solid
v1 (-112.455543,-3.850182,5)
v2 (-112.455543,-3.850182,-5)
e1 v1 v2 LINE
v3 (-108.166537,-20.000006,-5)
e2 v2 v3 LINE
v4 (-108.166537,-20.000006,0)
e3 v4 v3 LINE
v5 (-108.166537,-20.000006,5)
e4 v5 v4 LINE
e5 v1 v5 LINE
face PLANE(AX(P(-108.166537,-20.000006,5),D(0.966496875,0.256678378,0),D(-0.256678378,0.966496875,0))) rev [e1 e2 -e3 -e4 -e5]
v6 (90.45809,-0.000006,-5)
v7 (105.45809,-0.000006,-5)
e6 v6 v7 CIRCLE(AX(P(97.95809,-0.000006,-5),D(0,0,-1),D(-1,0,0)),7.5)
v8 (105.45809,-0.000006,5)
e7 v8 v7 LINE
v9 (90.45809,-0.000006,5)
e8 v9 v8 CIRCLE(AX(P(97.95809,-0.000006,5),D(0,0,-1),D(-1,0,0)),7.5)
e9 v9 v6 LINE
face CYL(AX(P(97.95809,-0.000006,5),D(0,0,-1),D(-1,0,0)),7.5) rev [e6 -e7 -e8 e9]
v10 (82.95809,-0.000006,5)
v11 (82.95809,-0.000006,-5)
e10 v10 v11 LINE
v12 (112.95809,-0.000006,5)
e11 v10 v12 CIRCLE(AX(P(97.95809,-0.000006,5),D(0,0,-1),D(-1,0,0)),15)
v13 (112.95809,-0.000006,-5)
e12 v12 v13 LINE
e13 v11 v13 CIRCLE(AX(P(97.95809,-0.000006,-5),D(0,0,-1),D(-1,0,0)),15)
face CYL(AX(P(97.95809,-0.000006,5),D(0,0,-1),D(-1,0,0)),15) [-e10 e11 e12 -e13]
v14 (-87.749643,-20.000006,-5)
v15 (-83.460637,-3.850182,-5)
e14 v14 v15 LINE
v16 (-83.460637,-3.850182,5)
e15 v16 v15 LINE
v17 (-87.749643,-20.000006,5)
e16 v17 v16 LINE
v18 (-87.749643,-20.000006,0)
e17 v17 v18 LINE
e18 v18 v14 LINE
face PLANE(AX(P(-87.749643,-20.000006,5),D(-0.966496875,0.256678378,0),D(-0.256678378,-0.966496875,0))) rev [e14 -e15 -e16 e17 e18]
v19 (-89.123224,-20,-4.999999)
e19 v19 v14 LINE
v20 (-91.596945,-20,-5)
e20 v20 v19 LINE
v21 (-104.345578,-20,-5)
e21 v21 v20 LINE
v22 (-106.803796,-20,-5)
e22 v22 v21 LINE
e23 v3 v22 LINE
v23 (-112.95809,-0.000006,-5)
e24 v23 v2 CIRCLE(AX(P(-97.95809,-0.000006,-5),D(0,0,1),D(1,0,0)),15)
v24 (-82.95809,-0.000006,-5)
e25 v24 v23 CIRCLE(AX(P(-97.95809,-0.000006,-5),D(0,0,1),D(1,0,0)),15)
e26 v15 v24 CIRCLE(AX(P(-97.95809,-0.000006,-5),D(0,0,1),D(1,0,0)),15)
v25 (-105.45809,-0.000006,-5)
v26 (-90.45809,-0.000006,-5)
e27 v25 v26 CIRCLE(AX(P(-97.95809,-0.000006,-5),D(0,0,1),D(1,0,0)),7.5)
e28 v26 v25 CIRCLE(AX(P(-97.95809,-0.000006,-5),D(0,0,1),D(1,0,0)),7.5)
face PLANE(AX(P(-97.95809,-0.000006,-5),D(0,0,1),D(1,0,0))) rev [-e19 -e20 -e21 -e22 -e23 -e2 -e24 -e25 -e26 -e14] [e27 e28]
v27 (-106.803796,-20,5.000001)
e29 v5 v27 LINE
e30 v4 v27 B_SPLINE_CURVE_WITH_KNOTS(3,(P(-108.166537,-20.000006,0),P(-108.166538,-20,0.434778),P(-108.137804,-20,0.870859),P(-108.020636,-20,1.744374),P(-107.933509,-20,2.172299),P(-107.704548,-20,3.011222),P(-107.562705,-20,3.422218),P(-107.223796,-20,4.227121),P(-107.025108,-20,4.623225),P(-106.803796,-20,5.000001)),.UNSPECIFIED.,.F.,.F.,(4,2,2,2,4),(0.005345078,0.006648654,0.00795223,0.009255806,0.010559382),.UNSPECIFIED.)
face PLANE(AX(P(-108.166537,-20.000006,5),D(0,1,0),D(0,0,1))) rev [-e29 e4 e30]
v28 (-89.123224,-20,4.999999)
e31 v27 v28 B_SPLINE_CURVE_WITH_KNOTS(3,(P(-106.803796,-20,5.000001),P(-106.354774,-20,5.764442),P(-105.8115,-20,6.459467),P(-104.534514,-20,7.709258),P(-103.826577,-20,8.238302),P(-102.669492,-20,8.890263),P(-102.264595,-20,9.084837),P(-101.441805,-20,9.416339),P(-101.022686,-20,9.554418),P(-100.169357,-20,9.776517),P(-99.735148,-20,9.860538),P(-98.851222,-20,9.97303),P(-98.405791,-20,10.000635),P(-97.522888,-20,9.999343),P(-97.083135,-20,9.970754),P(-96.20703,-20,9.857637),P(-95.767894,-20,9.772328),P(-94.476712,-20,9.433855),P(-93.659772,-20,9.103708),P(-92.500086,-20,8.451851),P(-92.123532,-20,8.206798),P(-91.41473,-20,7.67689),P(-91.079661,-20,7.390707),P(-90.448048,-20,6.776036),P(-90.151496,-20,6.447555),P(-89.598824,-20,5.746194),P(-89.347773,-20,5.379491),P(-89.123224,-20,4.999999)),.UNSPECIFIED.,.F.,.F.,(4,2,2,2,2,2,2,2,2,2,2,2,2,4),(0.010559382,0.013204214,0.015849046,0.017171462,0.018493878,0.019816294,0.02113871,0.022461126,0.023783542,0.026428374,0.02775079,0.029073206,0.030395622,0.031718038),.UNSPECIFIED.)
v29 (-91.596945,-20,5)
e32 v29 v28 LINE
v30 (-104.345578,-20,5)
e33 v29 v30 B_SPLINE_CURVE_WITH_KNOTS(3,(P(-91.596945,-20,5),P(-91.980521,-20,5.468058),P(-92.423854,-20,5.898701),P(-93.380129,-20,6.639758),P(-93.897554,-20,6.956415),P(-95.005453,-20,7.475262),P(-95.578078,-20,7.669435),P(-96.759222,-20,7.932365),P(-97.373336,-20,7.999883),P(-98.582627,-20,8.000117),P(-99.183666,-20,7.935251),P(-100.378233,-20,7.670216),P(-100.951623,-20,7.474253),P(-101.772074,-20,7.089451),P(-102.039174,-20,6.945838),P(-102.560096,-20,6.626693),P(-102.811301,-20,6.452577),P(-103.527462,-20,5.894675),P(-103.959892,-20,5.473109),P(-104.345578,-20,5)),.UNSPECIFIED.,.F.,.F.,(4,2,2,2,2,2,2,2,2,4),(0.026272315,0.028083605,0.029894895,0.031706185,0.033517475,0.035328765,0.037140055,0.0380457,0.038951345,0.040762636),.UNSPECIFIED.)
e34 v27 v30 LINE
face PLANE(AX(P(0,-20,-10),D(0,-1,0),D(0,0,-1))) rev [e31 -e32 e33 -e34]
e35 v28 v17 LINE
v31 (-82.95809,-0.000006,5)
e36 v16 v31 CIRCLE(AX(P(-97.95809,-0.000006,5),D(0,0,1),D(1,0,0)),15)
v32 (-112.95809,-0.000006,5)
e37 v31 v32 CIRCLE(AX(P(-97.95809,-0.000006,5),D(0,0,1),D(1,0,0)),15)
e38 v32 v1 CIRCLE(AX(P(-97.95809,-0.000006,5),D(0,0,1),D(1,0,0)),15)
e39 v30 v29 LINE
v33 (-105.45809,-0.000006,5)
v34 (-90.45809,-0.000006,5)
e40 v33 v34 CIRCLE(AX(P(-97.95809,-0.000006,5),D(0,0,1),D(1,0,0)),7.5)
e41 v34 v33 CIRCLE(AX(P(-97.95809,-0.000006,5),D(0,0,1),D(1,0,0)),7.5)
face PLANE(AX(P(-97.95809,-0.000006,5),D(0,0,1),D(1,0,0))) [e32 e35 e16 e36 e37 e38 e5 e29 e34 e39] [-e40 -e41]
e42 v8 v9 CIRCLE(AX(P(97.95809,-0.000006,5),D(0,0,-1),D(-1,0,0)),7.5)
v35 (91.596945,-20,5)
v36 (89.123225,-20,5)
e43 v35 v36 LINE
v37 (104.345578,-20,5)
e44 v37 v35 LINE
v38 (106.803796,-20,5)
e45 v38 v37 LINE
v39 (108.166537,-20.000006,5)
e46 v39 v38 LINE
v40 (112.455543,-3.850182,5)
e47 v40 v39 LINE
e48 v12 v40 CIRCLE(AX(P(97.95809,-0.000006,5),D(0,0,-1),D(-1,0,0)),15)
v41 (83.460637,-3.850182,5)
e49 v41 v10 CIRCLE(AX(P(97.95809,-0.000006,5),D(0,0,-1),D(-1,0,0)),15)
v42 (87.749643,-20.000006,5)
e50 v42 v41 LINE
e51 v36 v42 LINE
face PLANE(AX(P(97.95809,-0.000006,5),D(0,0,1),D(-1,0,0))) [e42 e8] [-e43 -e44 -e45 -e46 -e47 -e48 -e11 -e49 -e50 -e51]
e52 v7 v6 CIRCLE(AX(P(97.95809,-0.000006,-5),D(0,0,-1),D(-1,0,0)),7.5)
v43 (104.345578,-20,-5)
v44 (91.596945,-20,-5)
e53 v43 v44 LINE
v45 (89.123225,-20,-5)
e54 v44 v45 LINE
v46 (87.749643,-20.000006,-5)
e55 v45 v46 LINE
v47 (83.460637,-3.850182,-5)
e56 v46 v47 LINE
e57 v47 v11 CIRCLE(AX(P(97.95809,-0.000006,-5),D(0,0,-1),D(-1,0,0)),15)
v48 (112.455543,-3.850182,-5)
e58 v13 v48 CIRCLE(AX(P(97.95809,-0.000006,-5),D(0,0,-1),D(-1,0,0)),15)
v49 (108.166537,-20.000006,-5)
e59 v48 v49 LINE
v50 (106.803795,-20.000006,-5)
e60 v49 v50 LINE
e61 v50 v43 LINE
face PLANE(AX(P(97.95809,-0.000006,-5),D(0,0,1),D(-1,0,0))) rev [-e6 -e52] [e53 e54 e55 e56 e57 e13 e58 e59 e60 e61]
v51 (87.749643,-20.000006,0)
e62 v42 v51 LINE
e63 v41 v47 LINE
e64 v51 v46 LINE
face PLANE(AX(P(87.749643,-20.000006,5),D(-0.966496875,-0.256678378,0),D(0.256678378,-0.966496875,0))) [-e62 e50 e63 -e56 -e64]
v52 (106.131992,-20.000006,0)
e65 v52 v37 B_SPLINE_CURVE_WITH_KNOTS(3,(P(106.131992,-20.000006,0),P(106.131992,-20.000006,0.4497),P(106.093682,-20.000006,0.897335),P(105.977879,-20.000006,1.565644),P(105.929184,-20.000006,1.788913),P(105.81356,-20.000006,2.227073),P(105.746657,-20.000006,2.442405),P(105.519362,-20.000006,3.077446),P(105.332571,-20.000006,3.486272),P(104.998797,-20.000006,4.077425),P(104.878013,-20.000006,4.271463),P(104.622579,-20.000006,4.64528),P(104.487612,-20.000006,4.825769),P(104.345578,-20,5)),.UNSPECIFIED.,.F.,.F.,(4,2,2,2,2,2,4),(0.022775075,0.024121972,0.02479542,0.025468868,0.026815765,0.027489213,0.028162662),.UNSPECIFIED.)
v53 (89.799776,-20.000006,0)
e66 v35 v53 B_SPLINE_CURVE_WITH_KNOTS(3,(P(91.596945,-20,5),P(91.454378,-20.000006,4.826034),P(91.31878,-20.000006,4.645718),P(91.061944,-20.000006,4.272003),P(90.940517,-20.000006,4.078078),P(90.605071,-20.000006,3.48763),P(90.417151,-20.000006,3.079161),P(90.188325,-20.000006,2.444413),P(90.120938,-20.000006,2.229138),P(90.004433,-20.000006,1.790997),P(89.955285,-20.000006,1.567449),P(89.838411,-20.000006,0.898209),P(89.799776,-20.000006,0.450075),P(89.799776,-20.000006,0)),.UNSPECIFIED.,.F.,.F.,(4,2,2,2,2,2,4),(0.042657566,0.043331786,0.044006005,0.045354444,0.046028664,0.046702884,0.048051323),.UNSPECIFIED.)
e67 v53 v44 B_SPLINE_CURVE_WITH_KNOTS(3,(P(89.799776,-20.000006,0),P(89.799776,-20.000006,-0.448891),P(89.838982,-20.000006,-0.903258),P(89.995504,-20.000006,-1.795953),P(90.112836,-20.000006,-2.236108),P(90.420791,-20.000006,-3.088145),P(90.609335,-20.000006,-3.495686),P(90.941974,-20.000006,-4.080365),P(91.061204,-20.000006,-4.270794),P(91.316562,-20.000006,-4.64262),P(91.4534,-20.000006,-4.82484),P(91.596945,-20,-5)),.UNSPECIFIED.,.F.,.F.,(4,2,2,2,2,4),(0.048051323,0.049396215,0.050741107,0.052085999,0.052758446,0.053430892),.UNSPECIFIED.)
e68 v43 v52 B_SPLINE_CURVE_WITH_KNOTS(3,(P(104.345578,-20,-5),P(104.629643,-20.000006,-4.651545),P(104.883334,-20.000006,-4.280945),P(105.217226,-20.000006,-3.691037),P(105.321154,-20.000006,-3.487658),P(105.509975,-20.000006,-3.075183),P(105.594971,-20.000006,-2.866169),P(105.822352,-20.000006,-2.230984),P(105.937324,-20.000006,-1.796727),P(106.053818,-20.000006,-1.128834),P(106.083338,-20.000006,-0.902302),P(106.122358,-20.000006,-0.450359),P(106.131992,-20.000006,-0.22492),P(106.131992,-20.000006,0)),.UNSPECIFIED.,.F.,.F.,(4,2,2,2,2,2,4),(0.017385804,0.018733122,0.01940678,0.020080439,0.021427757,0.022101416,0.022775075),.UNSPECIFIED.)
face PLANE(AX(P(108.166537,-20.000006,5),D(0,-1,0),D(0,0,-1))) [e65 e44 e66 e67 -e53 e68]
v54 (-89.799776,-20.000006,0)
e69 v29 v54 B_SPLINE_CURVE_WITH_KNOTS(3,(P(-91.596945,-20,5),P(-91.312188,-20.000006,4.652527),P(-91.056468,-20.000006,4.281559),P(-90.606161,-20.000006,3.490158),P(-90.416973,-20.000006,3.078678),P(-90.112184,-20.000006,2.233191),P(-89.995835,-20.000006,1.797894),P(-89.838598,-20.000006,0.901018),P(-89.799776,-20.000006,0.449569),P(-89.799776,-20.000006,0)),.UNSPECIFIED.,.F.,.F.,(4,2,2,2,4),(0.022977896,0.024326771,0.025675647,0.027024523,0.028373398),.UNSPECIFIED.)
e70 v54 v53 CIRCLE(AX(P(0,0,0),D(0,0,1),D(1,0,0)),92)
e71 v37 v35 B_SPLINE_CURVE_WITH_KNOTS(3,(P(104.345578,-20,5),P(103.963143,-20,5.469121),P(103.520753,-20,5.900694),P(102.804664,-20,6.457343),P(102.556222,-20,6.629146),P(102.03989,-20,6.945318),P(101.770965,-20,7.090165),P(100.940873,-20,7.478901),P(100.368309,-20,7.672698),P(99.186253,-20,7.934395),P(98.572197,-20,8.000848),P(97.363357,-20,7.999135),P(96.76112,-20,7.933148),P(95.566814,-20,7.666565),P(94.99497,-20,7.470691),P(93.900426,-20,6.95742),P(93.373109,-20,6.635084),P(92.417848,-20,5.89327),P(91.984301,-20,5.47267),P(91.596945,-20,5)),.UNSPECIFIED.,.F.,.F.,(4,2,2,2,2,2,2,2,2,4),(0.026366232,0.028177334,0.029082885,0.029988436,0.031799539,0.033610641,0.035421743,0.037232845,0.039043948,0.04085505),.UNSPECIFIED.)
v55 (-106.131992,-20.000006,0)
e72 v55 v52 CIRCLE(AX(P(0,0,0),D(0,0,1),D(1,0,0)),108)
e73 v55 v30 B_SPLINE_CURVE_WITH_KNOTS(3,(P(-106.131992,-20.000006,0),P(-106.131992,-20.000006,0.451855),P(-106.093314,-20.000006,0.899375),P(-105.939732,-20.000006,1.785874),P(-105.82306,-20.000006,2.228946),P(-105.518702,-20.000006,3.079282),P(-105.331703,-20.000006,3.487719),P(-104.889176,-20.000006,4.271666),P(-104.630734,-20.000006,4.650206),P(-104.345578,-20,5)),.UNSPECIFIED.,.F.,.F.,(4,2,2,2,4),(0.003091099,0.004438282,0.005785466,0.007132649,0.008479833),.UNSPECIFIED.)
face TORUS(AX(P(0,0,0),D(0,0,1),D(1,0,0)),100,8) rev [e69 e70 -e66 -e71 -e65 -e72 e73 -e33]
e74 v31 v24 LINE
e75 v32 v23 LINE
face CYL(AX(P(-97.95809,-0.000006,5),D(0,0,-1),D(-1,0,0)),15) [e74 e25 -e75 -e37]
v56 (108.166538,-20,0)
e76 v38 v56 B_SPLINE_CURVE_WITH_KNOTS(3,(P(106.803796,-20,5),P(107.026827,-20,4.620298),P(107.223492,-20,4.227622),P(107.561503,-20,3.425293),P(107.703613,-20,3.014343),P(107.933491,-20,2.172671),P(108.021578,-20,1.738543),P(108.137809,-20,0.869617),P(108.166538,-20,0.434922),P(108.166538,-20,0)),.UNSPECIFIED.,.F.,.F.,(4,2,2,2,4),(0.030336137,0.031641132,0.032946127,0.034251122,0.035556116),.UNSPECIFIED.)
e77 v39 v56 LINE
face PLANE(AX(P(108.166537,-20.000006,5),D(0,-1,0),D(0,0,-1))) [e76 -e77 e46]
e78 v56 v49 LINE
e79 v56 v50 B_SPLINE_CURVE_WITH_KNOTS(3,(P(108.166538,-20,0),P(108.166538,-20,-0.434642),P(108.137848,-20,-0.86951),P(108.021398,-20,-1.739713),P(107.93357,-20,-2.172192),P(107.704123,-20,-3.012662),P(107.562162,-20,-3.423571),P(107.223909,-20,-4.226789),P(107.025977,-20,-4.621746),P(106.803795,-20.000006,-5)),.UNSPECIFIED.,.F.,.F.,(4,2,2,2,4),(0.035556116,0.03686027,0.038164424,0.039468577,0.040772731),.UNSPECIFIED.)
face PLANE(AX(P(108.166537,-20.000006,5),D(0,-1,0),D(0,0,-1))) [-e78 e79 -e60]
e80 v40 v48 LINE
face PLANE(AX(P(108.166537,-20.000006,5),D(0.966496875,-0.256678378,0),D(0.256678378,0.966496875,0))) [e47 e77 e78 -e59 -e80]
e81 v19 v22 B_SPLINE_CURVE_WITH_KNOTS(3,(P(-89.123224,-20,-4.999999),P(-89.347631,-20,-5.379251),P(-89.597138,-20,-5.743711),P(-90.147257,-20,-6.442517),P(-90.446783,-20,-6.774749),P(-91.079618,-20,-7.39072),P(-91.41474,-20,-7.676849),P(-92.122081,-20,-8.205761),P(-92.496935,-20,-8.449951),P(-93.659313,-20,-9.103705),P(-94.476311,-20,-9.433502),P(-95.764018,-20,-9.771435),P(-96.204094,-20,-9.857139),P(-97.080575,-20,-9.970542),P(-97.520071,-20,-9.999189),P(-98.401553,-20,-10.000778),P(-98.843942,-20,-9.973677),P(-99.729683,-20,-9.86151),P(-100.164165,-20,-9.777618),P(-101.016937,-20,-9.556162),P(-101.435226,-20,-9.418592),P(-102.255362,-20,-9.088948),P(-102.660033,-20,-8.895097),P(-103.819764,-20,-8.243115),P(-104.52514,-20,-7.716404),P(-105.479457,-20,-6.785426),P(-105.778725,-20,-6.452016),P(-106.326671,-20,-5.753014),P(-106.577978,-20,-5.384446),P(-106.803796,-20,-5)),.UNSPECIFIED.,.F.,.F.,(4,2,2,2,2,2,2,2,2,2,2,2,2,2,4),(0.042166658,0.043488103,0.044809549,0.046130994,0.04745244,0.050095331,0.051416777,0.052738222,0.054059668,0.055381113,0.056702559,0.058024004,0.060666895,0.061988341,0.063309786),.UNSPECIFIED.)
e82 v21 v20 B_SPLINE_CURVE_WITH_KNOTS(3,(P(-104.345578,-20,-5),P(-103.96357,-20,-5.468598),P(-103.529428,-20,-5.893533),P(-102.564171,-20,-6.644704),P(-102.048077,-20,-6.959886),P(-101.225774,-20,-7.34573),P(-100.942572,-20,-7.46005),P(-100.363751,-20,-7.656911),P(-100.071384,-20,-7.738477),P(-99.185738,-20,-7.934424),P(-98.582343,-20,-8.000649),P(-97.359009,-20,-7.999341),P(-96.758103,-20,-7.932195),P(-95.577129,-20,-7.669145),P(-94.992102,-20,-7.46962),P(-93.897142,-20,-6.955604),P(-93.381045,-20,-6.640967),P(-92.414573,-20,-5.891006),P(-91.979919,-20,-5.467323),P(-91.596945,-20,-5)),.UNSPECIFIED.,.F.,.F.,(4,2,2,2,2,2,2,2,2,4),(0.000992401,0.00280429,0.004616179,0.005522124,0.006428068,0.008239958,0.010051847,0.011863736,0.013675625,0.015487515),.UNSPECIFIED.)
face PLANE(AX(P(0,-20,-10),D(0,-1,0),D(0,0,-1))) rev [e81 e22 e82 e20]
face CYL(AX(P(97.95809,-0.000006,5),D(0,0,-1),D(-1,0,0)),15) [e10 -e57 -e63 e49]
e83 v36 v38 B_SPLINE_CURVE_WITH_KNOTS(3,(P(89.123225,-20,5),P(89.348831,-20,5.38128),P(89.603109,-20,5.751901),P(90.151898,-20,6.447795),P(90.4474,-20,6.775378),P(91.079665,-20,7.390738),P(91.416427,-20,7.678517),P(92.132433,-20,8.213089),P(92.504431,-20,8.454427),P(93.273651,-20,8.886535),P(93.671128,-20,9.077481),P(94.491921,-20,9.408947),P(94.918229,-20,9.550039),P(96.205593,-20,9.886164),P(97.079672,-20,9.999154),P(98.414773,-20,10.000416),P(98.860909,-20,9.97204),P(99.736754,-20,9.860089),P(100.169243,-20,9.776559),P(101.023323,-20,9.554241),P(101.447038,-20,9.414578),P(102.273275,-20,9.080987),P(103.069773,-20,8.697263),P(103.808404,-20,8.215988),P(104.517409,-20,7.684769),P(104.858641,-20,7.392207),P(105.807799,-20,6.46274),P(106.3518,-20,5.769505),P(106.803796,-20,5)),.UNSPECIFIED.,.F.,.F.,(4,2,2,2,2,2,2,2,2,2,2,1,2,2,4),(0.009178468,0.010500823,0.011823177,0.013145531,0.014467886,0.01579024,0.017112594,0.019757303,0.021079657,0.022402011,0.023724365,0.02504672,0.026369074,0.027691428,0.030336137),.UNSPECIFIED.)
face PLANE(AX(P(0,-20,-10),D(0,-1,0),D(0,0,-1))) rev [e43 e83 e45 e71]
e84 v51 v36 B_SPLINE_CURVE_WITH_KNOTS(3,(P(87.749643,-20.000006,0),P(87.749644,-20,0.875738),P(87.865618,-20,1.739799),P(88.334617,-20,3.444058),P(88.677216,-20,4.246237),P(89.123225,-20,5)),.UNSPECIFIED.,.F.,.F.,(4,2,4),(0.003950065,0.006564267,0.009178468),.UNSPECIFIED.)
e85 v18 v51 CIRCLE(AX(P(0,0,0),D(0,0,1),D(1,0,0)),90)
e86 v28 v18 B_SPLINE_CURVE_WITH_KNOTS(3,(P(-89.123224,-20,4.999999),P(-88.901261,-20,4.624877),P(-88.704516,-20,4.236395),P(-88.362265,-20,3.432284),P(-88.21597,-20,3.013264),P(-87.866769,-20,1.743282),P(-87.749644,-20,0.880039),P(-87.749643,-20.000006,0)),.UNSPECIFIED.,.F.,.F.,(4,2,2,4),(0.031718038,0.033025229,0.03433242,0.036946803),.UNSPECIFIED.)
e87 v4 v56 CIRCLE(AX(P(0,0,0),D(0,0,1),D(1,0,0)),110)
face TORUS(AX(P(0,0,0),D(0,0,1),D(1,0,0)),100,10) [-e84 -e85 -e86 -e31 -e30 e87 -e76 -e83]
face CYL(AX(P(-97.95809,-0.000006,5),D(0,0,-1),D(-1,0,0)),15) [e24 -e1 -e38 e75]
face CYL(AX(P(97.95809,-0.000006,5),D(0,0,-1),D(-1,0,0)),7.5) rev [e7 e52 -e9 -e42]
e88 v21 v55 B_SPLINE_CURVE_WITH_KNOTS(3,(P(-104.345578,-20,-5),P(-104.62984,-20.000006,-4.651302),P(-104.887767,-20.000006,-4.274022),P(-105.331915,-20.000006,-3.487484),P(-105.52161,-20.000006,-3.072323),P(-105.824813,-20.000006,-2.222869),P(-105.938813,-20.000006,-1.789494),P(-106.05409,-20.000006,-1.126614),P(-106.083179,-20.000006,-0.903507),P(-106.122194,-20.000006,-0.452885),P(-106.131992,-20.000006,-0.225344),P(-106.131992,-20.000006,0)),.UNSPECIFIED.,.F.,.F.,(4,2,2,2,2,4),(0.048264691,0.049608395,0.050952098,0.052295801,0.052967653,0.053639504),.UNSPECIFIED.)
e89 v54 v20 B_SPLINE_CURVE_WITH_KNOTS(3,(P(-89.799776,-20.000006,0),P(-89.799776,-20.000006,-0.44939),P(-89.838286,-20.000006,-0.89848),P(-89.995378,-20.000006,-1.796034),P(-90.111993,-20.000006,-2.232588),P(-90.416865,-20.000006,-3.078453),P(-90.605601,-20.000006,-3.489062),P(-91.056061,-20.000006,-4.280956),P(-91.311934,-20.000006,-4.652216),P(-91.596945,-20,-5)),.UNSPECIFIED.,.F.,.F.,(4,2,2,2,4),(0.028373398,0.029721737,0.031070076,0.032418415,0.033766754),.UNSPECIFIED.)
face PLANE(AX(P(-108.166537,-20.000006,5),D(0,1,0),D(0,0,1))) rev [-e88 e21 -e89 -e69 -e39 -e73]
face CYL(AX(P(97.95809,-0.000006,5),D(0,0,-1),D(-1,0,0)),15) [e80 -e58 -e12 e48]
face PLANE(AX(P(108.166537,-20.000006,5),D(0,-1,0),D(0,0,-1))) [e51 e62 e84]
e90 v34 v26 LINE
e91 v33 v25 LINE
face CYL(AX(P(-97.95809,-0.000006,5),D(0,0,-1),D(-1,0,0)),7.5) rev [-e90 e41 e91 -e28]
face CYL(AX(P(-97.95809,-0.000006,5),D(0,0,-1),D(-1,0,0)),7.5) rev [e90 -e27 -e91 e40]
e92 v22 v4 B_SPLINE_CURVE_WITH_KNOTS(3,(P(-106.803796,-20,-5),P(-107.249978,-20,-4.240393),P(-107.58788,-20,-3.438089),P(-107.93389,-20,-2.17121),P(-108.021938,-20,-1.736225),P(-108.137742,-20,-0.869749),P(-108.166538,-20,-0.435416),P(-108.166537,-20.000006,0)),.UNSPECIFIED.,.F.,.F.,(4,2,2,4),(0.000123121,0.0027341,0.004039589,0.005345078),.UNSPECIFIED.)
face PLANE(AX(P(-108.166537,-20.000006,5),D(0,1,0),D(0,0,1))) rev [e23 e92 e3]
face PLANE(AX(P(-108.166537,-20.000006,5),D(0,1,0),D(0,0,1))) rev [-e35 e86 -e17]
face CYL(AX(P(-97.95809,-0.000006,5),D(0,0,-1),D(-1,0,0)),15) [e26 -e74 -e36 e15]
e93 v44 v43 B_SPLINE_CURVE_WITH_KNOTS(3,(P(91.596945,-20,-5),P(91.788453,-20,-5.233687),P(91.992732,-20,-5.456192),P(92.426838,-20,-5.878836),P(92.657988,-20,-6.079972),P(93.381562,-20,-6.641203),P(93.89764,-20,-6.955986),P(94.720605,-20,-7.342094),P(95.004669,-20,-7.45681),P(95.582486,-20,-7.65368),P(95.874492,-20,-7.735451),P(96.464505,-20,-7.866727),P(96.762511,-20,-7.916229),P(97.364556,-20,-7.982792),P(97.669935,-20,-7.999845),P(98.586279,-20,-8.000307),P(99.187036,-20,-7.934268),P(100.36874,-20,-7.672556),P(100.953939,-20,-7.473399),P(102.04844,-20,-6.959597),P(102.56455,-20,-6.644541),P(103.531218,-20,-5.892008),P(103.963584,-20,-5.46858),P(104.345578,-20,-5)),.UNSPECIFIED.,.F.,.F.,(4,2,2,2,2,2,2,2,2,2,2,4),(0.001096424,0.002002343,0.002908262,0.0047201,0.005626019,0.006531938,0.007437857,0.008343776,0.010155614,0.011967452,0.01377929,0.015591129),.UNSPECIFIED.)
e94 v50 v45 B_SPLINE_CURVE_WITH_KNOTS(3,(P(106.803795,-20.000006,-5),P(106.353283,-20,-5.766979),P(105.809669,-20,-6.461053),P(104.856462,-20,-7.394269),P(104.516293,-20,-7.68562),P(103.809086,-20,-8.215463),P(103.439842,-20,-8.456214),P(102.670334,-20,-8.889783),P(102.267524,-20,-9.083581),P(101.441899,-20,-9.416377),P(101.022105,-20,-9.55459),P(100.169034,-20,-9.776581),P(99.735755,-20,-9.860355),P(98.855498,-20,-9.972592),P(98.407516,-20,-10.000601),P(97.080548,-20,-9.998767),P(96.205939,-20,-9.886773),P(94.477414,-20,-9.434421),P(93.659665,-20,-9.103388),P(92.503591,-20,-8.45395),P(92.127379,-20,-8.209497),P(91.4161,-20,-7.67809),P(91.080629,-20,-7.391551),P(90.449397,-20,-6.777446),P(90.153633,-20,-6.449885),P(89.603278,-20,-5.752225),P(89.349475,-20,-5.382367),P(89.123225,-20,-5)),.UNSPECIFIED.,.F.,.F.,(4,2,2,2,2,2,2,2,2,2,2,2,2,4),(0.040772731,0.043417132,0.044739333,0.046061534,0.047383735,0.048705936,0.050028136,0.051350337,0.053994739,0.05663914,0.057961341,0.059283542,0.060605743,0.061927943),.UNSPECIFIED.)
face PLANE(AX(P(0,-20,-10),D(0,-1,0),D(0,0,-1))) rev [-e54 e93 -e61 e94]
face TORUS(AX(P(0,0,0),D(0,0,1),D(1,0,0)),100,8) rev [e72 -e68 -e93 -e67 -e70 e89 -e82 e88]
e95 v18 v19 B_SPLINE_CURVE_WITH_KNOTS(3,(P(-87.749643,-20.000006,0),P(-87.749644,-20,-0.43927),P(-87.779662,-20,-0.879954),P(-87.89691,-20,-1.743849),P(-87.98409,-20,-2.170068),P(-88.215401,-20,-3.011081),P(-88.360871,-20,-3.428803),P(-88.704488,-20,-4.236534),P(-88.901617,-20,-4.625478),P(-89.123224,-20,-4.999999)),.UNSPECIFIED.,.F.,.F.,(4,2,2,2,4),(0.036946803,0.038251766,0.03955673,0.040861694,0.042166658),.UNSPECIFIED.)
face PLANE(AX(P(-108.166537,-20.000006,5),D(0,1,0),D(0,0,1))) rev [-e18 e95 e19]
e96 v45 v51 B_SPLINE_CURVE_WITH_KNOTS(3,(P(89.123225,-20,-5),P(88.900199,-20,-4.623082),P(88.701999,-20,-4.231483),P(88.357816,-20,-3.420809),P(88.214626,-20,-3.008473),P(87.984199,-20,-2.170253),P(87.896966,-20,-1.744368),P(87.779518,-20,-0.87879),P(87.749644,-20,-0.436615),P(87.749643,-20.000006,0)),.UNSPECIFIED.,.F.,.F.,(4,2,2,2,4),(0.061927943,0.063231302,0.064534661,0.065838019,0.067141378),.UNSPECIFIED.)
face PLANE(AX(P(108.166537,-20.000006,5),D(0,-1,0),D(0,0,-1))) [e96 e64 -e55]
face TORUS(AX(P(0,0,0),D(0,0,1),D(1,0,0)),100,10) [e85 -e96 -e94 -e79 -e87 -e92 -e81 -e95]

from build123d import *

# Parameters (mm, degrees)
SKETCH_2_R               = 10
SKETCH_2_R_2             = 8
CUT_EXTRUDE_1_DEPTH      = 156.884572829
CUT_EXTRUDE_1_DEPTH_BACK = 156.884572829
SKETCH_4_R               = 7.5
EXTRUDE_1_DEPTH          = 5


with BuildPart() as part:
    # 扫描1: sweep along a path in 草图1
    with BuildLine(Plane.XY) as sweep_1_path:
        CenterArc((0, 0), 100, 0, 360)
    # 草图2 → 扫描1 (sweep)
    with BuildSketch(Plane(origin=(0, 0, 0), x_dir=(0, 0, -1), z_dir=(1, 0, 0))):
        with Locations((0, -100)):
            Circle(SKETCH_2_R)
        with Locations((0, -100)):
            Circle(SKETCH_2_R_2, mode=Mode.SUBTRACT)
    sweep(path=sweep_1_path.line)

    # 草图3 → 切除-拉伸1 (cut, two sides: drawn at the far end of the back side and taken through both)
    with BuildSketch(Plane.XY.offset(-CUT_EXTRUDE_1_DEPTH_BACK)):
        Polygon((-124.821104754, -20), (0, -20), (127.823184446, -20), (127.823184446, 142.660997567), (-124.821104754, 142.660997567), align=None)
    extrude(amount=CUT_EXTRUDE_1_DEPTH + CUT_EXTRUDE_1_DEPTH_BACK, mode=Mode.SUBTRACT)

    # 草图4 → 凸台-拉伸1 (add, symmetric)
    with BuildSketch(Plane.XY):
        with BuildLine():
            Line((-108.166537158, -20.000005979), (-112.455542967, -3.850181648))
            ThreePointArc((-112.455542967, -3.850181648), (-97.958089835, 14.999994021), (-83.460636703, -3.850181648))
            Line((-83.460636703, -3.850181648), (-87.749642511, -20.000005979))
            Line((-87.749642511, -20.000005979), (-108.166537158, -20.000005979))
        make_face()
        with Locations((-97.958089835, -5.979e-06)):
            Circle(SKETCH_4_R, mode=Mode.SUBTRACT)
    extrude_1 = extrude(amount=EXTRUDE_1_DEPTH, both=True)

    # 镜向1: 凸台-拉伸1 across plane
    add(extrude_1.mirror(Plane(origin=(0, 0, 0), x_dir=(0, 0, 1), z_dir=(1, 0, 0))))


solid = part.part
